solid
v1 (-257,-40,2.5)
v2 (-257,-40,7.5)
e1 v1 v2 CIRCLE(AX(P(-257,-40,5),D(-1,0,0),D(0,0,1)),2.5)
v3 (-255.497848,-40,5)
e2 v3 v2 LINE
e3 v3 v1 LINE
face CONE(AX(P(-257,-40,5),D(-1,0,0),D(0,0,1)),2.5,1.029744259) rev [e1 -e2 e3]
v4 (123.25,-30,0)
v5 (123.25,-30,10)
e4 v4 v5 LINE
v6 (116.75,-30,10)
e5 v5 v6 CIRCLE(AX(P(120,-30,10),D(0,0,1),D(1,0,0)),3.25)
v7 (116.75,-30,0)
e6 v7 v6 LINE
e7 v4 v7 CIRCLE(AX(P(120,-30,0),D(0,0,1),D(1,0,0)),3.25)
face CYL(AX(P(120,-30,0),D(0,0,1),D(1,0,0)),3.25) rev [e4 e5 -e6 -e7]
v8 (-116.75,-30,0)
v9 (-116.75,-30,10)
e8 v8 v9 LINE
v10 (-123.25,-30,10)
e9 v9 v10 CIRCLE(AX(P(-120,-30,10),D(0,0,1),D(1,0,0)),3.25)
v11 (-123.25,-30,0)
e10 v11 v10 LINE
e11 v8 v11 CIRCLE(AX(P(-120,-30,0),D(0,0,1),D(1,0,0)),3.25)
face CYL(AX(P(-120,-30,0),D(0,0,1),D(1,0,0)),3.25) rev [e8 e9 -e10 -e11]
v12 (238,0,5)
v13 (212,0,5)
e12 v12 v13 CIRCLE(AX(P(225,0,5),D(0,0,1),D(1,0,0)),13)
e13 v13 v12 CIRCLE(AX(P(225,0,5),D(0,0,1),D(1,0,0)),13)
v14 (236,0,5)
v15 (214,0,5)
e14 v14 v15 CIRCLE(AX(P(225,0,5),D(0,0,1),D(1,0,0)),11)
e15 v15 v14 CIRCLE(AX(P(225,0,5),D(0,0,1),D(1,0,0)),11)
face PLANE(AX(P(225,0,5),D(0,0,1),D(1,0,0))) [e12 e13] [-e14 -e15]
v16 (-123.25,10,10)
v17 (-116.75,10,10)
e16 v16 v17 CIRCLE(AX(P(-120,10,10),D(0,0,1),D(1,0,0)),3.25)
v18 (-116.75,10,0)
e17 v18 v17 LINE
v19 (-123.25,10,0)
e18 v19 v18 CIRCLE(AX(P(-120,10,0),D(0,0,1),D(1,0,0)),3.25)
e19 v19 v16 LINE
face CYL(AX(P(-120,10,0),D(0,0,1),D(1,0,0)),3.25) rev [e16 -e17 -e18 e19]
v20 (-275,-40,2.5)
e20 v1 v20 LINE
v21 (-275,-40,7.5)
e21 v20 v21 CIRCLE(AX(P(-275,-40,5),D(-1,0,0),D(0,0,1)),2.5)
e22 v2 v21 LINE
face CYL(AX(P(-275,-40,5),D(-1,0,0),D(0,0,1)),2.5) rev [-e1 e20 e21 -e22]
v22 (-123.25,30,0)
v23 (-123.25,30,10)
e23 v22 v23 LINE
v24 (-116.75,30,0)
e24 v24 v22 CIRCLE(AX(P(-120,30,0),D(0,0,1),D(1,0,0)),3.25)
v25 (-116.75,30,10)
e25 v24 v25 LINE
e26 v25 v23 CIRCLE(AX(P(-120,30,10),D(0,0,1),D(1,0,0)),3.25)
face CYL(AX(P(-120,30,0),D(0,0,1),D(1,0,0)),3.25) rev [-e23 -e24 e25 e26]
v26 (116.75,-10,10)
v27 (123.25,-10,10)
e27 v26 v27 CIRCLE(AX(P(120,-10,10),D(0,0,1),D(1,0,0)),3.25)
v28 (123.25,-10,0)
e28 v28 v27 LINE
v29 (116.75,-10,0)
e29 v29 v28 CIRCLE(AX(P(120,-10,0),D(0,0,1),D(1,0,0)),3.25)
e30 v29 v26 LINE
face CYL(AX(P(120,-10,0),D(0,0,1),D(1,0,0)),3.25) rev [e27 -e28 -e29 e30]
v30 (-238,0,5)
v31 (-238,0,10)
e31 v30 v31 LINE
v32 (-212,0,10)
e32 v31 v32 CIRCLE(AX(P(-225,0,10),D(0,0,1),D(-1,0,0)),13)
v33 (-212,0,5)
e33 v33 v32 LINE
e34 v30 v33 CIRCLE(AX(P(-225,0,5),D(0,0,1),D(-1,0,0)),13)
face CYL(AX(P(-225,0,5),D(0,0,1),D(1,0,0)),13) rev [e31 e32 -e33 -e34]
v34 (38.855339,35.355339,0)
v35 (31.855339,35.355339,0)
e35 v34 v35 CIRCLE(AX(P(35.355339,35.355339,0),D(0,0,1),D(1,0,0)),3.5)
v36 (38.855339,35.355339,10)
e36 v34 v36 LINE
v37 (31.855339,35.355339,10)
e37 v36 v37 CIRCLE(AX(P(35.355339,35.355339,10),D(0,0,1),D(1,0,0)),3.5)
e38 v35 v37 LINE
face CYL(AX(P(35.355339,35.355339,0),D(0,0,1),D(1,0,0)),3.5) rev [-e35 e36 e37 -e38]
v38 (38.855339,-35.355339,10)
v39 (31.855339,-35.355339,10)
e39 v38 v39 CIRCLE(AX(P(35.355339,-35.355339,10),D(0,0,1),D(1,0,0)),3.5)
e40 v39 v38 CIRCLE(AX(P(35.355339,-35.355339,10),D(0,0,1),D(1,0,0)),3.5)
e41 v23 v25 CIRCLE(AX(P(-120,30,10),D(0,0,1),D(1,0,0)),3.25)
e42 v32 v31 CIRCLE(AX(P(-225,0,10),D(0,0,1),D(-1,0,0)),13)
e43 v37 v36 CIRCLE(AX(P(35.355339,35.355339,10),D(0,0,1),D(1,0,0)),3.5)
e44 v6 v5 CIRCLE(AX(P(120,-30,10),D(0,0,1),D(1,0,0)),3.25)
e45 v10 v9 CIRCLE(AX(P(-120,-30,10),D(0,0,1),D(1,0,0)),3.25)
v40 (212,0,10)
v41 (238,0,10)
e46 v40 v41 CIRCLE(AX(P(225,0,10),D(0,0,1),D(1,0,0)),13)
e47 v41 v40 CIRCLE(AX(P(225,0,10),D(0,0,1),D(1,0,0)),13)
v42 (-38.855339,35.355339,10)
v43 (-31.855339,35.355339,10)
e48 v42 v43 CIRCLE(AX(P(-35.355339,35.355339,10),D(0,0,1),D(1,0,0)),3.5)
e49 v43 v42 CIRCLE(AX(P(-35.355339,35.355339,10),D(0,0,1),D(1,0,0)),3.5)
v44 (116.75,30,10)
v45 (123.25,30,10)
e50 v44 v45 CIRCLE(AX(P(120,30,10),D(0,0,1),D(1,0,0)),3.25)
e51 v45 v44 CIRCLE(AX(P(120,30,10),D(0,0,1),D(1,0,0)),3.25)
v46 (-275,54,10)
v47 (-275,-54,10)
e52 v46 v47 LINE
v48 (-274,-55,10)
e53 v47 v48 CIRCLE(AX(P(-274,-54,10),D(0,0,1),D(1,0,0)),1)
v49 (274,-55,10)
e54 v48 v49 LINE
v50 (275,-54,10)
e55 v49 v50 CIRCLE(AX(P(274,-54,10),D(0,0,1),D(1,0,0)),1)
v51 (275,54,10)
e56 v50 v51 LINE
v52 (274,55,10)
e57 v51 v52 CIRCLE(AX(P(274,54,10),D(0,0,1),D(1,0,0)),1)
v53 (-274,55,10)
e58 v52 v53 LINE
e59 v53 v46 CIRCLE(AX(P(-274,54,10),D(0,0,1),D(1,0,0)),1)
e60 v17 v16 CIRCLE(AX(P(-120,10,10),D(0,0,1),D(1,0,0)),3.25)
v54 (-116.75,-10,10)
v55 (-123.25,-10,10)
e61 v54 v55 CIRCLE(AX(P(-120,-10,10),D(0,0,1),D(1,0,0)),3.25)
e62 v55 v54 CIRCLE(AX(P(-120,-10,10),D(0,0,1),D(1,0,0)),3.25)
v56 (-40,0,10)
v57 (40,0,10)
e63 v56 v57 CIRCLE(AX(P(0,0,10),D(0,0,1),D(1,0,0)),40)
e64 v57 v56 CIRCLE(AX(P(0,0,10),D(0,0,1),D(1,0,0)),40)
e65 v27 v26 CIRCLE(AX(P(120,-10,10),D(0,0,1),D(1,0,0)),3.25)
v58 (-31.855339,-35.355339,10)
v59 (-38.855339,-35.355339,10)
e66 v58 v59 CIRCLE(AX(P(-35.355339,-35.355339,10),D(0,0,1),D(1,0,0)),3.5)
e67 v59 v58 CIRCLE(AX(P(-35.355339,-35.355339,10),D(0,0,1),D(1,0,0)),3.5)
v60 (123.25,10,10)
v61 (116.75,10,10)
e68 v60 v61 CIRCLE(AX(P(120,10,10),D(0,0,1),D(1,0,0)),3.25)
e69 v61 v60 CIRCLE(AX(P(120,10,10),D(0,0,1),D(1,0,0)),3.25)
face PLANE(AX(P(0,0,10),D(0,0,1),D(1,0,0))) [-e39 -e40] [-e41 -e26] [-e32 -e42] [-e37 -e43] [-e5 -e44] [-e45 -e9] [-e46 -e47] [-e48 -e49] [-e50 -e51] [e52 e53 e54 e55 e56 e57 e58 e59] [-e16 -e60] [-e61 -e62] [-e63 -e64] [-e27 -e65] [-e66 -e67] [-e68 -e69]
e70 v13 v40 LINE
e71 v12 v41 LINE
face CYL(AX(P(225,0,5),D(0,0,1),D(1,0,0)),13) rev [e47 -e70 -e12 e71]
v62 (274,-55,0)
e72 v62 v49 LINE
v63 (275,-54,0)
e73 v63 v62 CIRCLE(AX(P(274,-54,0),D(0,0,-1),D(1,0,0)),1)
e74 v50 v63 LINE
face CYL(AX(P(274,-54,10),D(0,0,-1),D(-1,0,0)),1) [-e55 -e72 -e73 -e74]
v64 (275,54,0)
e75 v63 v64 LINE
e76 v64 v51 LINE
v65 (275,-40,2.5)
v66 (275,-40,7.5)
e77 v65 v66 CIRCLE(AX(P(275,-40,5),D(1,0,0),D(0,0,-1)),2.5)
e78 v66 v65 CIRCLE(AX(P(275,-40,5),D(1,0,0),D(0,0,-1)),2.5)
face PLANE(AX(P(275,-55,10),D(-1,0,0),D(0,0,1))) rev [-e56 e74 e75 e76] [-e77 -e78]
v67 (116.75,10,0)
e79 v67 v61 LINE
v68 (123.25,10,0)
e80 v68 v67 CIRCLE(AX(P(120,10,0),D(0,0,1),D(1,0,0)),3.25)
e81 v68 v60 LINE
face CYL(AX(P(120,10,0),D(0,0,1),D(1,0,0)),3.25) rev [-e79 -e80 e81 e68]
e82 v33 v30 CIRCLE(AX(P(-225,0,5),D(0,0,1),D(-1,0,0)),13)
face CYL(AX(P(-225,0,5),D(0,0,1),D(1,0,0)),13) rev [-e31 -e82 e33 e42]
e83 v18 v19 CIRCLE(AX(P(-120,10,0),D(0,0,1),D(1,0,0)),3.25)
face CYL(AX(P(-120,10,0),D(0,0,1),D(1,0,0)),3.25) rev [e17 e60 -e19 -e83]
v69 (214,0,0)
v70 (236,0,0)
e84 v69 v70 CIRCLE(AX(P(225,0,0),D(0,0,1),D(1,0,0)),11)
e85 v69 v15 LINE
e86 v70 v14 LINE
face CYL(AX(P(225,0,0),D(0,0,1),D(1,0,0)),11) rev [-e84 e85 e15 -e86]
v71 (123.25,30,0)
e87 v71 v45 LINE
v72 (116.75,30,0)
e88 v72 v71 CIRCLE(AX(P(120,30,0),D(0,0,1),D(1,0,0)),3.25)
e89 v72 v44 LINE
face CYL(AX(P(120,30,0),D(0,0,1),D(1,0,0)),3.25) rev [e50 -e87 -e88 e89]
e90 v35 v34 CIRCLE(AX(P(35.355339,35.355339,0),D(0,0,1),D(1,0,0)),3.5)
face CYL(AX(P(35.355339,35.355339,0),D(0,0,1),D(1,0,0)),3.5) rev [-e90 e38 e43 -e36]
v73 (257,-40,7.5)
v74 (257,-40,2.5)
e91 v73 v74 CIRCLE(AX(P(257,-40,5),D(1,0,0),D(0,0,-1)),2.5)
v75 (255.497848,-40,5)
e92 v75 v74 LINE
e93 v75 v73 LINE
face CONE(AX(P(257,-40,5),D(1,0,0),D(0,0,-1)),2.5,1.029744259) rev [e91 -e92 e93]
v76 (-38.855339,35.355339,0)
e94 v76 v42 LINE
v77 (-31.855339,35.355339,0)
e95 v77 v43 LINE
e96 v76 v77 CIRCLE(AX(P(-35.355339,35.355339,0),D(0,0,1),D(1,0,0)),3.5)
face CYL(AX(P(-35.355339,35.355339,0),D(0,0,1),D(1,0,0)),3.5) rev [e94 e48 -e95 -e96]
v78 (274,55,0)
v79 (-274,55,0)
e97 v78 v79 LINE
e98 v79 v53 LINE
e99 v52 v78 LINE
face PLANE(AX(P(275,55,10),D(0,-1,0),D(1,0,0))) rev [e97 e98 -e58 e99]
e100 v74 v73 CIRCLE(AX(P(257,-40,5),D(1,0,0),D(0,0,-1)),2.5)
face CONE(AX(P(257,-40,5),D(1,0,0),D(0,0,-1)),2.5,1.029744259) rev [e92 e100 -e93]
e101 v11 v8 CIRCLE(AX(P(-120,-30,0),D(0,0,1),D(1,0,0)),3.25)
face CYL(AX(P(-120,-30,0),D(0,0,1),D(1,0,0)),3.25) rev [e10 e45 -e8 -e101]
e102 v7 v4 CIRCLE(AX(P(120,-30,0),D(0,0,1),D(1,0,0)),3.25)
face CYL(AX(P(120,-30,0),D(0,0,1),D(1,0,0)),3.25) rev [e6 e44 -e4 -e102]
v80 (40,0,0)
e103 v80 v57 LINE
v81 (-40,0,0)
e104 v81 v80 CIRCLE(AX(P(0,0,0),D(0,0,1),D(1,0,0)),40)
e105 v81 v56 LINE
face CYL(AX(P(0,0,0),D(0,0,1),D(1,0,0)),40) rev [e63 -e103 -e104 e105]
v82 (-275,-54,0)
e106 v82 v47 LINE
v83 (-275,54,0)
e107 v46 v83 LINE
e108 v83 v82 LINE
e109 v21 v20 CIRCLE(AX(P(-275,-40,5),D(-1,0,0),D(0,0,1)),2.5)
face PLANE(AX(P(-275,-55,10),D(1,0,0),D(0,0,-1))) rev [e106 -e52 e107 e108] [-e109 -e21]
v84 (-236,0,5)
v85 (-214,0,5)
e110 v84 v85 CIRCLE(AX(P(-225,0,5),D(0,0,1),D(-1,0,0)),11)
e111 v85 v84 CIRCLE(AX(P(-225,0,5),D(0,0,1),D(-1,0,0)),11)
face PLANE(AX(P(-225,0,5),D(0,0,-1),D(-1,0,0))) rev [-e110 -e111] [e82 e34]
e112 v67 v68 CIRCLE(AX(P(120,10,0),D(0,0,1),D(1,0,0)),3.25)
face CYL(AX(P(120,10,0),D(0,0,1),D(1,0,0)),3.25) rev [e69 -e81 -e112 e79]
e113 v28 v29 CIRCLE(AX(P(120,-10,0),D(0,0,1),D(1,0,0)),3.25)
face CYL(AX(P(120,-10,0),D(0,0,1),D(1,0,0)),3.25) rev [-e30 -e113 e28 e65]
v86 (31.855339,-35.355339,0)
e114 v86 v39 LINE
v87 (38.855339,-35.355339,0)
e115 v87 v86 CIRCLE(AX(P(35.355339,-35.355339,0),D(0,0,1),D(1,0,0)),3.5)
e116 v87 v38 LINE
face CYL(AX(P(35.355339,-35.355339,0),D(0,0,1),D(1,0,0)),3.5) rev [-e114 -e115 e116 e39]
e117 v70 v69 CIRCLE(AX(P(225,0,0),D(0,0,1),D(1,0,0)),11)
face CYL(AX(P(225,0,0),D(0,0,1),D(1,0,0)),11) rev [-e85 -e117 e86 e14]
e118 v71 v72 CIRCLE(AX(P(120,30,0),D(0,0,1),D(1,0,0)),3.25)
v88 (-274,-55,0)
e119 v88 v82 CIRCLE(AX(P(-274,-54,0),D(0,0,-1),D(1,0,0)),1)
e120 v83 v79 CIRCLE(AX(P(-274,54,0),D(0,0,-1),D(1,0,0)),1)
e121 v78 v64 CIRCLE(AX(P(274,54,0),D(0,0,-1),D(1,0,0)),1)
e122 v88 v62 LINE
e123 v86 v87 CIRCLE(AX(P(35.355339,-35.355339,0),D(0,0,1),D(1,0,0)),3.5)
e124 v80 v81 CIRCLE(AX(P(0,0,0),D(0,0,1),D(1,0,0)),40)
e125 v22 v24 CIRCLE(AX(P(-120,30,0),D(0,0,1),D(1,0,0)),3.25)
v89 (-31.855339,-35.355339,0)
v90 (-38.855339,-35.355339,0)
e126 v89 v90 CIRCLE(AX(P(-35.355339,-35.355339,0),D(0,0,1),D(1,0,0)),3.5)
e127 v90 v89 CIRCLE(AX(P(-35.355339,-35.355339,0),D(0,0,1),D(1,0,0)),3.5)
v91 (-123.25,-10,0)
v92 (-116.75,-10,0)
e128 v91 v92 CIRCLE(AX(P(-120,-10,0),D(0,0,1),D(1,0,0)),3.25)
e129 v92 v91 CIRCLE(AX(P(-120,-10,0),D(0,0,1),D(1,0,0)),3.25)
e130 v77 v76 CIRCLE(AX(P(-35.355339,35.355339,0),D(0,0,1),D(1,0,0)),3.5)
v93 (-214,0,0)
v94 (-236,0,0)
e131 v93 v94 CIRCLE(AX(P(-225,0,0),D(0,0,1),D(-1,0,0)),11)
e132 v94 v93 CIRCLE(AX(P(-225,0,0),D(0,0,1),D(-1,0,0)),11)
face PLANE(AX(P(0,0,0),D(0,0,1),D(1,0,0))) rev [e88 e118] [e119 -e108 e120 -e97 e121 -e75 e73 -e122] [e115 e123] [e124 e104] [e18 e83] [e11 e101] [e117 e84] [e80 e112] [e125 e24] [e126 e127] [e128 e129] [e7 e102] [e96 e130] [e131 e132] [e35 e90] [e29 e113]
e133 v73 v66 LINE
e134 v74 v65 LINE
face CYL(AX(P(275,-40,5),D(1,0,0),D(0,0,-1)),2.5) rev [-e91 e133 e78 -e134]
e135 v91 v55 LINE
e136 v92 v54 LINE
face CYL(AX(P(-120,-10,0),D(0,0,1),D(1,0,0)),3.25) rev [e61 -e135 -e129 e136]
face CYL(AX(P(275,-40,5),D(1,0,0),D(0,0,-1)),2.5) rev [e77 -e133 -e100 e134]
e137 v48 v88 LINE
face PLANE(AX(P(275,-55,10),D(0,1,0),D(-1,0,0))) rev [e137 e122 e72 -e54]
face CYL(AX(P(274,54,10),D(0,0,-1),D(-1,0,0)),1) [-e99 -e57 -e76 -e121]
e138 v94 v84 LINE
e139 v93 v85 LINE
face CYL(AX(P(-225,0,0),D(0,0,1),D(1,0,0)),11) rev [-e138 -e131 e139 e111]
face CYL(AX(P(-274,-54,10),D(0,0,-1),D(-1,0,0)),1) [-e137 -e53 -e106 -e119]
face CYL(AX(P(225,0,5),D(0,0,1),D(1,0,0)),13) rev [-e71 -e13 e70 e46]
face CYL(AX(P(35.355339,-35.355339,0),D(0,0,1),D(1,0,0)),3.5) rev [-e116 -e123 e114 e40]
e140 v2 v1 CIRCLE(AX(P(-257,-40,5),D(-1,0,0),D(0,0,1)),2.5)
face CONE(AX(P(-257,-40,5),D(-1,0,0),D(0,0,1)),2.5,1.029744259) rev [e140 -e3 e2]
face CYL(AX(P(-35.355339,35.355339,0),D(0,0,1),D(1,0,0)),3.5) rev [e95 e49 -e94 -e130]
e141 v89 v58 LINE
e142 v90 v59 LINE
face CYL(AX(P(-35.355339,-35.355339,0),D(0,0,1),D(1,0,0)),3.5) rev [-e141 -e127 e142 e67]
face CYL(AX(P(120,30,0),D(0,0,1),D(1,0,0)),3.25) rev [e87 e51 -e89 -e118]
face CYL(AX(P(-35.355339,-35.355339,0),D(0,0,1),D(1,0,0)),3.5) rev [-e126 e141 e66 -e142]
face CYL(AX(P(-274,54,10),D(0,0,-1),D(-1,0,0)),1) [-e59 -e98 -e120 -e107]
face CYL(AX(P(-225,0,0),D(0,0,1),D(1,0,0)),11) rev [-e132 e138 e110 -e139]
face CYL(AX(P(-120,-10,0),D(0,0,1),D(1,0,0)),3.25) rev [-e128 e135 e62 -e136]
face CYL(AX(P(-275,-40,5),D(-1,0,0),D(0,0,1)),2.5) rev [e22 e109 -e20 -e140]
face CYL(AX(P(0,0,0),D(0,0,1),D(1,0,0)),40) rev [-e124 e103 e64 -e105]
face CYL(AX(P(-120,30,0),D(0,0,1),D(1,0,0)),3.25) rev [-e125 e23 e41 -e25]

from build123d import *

# Parameters (mm, degrees)
SKETCH1_W           = 550
SKETCH1_H           = 110
BOSS_EXTRUDE1_DEPTH = 10
SKETCH3_R           = 13
CUT_EXTRUDE2_DEPTH  = 5
SKETCH4_R           = 11
CUT_EXTRUDE3_DEPTH  = 281.490641555
SKETCH5_R           = 40
CUT_EXTRUDE4_DEPTH  = 281.624304008
SKETCH6_R           = 3.5
CUT_EXTRUDE5_DEPTH  = 281.624304008
SKETCH7_R           = 3.25
CUT_EXTRUDE6_DEPTH  = 281.624304008
FILLET1_R           = 1


with BuildPart() as part:
    # Sketch1 → Boss-Extrude1 (new body)
    with BuildSketch(Plane.XY):
        Rectangle(SKETCH1_W, SKETCH1_H)
    extrude(amount=BOSS_EXTRUDE1_DEPTH)

    # Sketch3 → Cut-Extrude2 (cut)
    with BuildSketch(Plane.XY.offset(10)):
        with Locations((225, 0)):
            Circle(SKETCH3_R)
        with Locations(Location((-225, 0, 0), (0, 0, 180))):
            Circle(SKETCH3_R)
    extrude(amount=-CUT_EXTRUDE2_DEPTH, mode=Mode.SUBTRACT)

    # Sketch4 → Cut-Extrude3 (cut, through all)
    with BuildSketch(Plane.XY.offset(5)):
        with Locations((225, 0)):
            Circle(SKETCH4_R)
        with Locations(Location((-225, 0, 0), (0, 0, 180))):
            Circle(SKETCH4_R)
    extrude(amount=-CUT_EXTRUDE3_DEPTH, mode=Mode.SUBTRACT)

    # Sketch5 → Cut-Extrude4 (cut, through all)
    with BuildSketch(Plane.XY.offset(10)):
        Circle(SKETCH5_R)
    extrude(amount=-CUT_EXTRUDE4_DEPTH, mode=Mode.SUBTRACT)

    # Sketch6 → Cut-Extrude5 (cut, through all)
    with BuildSketch(Plane.XY.offset(10)):
        with Locations((-35.355339059, 35.355339059)):
            Circle(SKETCH6_R)
        with Locations((35.355339059, 35.355339059)):
            Circle(SKETCH6_R)
        with Locations((35.355339059, -35.355339059)):
            Circle(SKETCH6_R)
        with Locations((-35.355339059, -35.355339059)):
            Circle(SKETCH6_R)
    extrude(amount=-CUT_EXTRUDE5_DEPTH, mode=Mode.SUBTRACT)

    # Sketch7 → Cut-Extrude6 (cut, through all)
    with BuildSketch(Plane.XY.offset(10)):
        with Locations((-120, -10)):
            Circle(SKETCH7_R)
        with Locations((120, -10)):
            Circle(SKETCH7_R)
        with Locations((120, 10)):
            Circle(SKETCH7_R)
        with Locations((-120, 10)):
            Circle(SKETCH7_R)
        with Locations((-120, -30)):
            Circle(SKETCH7_R)
        with Locations((-120, 30)):
            Circle(SKETCH7_R)
        with Locations((120, 30)):
            Circle(SKETCH7_R)
        with Locations((120, -30)):
            Circle(SKETCH7_R)
    extrude(amount=-CUT_EXTRUDE6_DEPTH, mode=Mode.SUBTRACT)

    # Fillet1
    fillet1_edges = [part.edges().sort_by_distance(p)[0] for p in [
        (-275, 55, 5),
        (275, 55, 5),
        (275, -55, 5),
        (-275, -55, 5),
    ]]
    fillet(fillet1_edges, radius=FILLET1_R)

    # Sketch9 → M6 Tapped Hole1 (revolve, cut)
    with BuildSketch(Plane(origin=(-275, -40, 5), x_dir=(0, 0, 1), z_dir=(0, 1, 0))):
        Polygon((0, 0), (0, 19.502151548), (2.5, 18), (2.5, 0), align=None)
    m6_tapped_hole1 = revolve(axis=Axis((-281.35, -40, 5), (1, 0, 0)), mode=Mode.SUBTRACT)

    # Mirror1: M6 Tapped Hole1 across plane
    add(m6_tapped_hole1.mirror(Plane(origin=(0, 0, 0), x_dir=(0, 0, 1), z_dir=(1, 0, 0))), mode=Mode.SUBTRACT)


solid = part.part
